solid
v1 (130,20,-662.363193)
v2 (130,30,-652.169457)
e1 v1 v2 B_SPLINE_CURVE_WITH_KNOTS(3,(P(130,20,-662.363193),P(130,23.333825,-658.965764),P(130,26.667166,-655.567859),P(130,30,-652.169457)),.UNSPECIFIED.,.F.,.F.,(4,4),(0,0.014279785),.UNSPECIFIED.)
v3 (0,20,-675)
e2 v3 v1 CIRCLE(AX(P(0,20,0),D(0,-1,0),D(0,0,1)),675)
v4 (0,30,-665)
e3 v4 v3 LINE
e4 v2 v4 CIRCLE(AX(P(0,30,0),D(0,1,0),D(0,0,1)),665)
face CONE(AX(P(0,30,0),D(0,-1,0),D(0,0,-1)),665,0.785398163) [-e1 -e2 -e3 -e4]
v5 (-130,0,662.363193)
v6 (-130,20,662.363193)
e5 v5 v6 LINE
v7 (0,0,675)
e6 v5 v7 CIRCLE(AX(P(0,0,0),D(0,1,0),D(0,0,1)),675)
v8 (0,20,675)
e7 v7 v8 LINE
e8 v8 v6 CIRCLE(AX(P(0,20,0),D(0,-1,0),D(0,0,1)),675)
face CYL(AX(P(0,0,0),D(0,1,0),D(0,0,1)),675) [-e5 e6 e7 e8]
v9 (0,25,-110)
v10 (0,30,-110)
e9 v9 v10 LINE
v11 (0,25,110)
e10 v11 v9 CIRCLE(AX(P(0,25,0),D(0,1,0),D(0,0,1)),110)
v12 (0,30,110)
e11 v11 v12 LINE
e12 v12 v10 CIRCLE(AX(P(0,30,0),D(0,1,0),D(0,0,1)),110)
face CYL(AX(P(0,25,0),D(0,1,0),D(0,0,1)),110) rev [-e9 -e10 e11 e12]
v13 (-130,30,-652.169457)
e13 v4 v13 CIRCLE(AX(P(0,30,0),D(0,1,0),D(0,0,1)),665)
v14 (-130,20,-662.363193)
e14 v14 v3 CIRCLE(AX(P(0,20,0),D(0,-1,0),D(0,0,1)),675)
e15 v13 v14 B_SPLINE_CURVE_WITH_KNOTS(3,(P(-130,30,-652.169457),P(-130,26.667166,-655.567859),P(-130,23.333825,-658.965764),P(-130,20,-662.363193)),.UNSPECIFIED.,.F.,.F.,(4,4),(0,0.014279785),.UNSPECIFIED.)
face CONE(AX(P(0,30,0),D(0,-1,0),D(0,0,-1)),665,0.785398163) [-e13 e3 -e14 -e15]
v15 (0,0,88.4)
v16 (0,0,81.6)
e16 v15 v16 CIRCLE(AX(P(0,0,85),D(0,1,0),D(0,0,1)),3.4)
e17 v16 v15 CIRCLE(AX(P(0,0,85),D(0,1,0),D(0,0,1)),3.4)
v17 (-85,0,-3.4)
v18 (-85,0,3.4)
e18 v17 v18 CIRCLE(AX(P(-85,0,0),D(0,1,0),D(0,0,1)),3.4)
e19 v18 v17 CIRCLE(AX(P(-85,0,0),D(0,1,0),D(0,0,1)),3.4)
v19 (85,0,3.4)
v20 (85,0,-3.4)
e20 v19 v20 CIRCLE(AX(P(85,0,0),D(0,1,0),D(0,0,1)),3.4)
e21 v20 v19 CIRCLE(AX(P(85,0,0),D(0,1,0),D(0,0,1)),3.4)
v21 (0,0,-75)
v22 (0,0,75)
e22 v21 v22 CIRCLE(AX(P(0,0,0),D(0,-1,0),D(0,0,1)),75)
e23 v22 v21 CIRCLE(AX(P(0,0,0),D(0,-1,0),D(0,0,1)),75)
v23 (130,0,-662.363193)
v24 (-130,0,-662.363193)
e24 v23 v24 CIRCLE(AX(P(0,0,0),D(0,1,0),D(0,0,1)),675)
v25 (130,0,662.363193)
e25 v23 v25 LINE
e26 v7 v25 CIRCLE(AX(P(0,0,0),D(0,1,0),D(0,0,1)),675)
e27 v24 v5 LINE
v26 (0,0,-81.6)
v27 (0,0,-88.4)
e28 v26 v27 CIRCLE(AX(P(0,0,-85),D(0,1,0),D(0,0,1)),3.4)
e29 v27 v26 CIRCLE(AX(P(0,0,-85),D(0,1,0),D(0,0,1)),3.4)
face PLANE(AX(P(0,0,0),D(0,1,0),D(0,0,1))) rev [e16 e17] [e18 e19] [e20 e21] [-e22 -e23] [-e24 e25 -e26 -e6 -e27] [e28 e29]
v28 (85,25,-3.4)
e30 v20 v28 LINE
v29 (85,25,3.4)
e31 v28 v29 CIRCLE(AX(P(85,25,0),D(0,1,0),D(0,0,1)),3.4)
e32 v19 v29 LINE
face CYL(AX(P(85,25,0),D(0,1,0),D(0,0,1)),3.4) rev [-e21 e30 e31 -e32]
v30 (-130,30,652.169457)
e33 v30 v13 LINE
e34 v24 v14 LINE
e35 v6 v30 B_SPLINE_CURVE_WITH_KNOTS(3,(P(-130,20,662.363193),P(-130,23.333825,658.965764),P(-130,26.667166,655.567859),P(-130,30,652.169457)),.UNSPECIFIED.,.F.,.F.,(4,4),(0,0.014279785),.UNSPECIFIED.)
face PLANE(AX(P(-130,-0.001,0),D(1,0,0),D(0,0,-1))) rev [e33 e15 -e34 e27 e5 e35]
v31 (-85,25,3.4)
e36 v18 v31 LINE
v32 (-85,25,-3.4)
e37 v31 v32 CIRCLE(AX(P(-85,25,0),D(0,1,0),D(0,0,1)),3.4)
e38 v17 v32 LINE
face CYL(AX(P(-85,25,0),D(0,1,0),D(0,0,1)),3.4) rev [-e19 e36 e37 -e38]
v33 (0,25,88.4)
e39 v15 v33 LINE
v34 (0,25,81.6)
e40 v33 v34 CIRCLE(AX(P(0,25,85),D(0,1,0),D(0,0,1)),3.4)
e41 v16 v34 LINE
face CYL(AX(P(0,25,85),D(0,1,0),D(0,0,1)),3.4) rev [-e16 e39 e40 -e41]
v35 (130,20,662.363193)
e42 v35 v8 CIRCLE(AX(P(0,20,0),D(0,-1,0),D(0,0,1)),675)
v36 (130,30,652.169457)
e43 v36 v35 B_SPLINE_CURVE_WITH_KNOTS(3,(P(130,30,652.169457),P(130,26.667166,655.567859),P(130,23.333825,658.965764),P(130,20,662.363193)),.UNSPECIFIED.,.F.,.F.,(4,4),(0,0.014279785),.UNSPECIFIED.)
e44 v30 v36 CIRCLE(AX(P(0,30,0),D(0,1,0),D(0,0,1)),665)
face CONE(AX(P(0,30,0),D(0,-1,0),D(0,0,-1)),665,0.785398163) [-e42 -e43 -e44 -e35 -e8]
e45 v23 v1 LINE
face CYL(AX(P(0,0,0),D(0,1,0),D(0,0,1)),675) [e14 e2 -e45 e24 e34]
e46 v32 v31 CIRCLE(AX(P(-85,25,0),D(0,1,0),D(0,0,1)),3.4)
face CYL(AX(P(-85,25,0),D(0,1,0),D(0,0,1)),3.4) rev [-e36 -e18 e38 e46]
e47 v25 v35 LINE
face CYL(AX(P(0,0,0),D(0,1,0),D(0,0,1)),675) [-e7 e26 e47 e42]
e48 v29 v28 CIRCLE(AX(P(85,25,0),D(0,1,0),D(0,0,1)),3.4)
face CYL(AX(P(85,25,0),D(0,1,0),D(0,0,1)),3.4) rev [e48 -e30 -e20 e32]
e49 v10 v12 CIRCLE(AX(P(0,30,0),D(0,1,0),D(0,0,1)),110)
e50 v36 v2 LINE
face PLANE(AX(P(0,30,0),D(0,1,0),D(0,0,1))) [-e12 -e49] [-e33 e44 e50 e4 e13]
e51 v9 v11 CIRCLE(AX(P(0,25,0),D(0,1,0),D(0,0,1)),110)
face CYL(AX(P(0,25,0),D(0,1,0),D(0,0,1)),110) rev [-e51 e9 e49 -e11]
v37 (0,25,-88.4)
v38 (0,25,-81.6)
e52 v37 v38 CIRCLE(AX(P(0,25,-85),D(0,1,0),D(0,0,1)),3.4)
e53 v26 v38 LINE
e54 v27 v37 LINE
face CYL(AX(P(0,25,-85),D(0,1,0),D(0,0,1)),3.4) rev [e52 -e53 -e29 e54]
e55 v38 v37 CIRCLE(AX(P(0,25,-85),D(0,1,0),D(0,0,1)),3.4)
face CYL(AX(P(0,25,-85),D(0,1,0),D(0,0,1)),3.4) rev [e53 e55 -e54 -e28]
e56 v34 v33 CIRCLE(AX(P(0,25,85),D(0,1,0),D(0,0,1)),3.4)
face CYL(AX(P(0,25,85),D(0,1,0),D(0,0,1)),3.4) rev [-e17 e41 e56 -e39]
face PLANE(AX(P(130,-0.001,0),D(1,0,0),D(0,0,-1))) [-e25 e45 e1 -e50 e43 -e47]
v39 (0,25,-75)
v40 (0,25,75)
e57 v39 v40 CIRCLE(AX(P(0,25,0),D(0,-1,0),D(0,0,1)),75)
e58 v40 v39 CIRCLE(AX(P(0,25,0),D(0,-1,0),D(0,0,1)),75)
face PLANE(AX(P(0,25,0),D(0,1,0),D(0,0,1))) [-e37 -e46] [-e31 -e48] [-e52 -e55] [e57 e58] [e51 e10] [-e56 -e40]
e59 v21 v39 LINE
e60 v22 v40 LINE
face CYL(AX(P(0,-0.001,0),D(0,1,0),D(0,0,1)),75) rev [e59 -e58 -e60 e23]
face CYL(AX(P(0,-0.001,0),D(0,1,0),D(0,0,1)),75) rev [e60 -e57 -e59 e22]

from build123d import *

# Parameters (mm, degrees)
SKETCH_1_R                = 810
EXTRUDE_1_DEPTH           = 25
SKETCH_2_R                = 730
EXTRUDE_2_DEPTH           = 5
CUT_EXTRUDE_1_REACH       = 1147.906
SKETCH_3_R                = 75
SKETCH_4_R                = 110
CUT_EXTRUDE_2_DEPTH       = 5
HOLE_WIZARD_M8_1_D        = 6.8
HOLE_WIZARD_25_5_25_5_1_D = 26
CUT_EXTRUDE_3_DEPTH       = 1146.905755287
CUT_EXTRUDE_3_DEPTH_BACK  = 1146.905755287
SKETCH_10_OUTSIDE_W       = 2080.244
SKETCH_10_OUTSIDE_H       = 2080.244
SKETCH_10_OUTSIDE_R       = 675
CHAMFER_1_SIZE            = 10


with BuildPart() as part:
    # 草图1 → 凸台-拉伸1 (new body)
    with BuildSketch(Plane(origin=(0, 0, 0), x_dir=(1, 0, 0), z_dir=(0, 1, 0))):
        with Locations(Location((0, 0, 0), (0, 0, 270))):
            Circle(SKETCH_1_R)
    extrude(amount=EXTRUDE_1_DEPTH)

    # 草图2 → 凸台-拉伸2 (add)
    with BuildSketch(Plane(origin=(0, 25, 0), x_dir=(1, 0, 0), z_dir=(0, 1, 0))):
        with Locations(Location((0, 0, 0), (0, 0, 270))):
            Circle(SKETCH_2_R)
    extrude(amount=EXTRUDE_2_DEPTH)

    # 草图3 → 切除-拉伸1 (cut, up to next)
    with BuildSketch(Plane(origin=(0, 30, 0), x_dir=(1, 0, 0), z_dir=(0, 1, 0)), mode=Mode.PRIVATE) as cut_extrude_1_sk1:
        with BuildLine():
            Line((130, 662.363193422), (130, -662.363193422))
            ThreePointArc((130, -662.363193422), (521.236510617, -428.879353665), (675, 0))
            ThreePointArc((675, 0), (521.236510617, 428.879353665), (130, 662.363193422))
        make_face()
    cut_extrude_1_tool1 = extrude(cut_extrude_1_sk1.sketch, amount=-CUT_EXTRUDE_1_REACH, mode=Mode.PRIVATE) & part.part
    # 草图3 → 切除-拉伸1 (cut, up to next)
    with BuildSketch(Plane(origin=(0, 30, 0), x_dir=(1, 0, 0), z_dir=(0, 1, 0)), mode=Mode.PRIVATE) as cut_extrude_1_sk2:
        with BuildLine():
            ThreePointArc((-130, 662.363193422), (-675, 0), (-130, -662.363193422))
            Line((-130, -662.363193422), (-130, 662.363193422))
        make_face()
    cut_extrude_1_tool2 = extrude(cut_extrude_1_sk2.sketch, amount=-CUT_EXTRUDE_1_REACH, mode=Mode.PRIVATE) & part.part
    # 草图3 → 切除-拉伸1 (cut, up to next)
    with BuildSketch(Plane(origin=(0, 30, 0), x_dir=(1, 0, 0), z_dir=(0, 1, 0)), mode=Mode.PRIVATE) as cut_extrude_1_sk3:
        with Locations(Location((0, 0, 0), (0, 0, 270))):
            Circle(SKETCH_3_R)
    cut_extrude_1_tool3 = extrude(cut_extrude_1_sk3.sketch, amount=-CUT_EXTRUDE_1_REACH, mode=Mode.PRIVATE) & part.part
    add(cut_extrude_1_tool1.solids().sort_by_distance((357.907844, 30, 0))[0], mode=Mode.SUBTRACT)
    add(cut_extrude_1_tool2.solids().sort_by_distance((-357.907844, 30, 0))[0], mode=Mode.SUBTRACT)
    add(cut_extrude_1_tool3.solids().sort_by_distance((0, 30, 0))[0], mode=Mode.SUBTRACT)

    # 草图4 → 切除-拉伸2 (cut)
    with BuildSketch(Plane(origin=(0, 30, 0), x_dir=(1, 0, 0), z_dir=(0, 1, 0))):
        with Locations(Location((0, 0, 0), (0, 0, 270))):
            Circle(SKETCH_4_R)
    extrude(amount=-CUT_EXTRUDE_2_DEPTH, mode=Mode.SUBTRACT)

    # M8 螺纹孔1 (through all)
    with Locations(Plane(origin=(0, 25, 0), x_dir=(1, 0, 0), z_dir=(0, 1, 0))):
        with Locations((0, 85), (85, 0), (0, -85), (-85, 0)):
            Hole(HOLE_WIZARD_M8_1_D / 2)

    # Ø25.5 (25.5) 直径孔1 (through all)
    with Locations(Plane(origin=(0, 25, 0), x_dir=(1, 0, 0), z_dir=(0, 1, 0))):
        with Locations((-59.354305918, 754.167962969), (59.354305918, 754.167962969), (176.601417757, 735.597844781), (289.500016584, 698.914866345), (395.270164208, 645.022284334), (491.307448562, 575.247112976), (575.247112976, 491.307448562), (645.022284334, 395.270164208), (698.914866345, 289.500016584), (735.597844781, 176.601417757), (754.167962969, 59.354305918), (754.167962969, -59.354305918), (735.597844781, -176.601417757), (698.914866345, -289.500016584), (645.022284334, -395.270164208), (575.247112976, -491.307448562), (491.307448562, -575.247112976), (395.270164208, -645.022284334), (289.500016584, -698.914866345), (176.601417757, -735.597844781), (59.354305918, -754.167962969), (-59.354305918, -754.167962969), (-176.601417757, -735.597844781), (-289.500016584, -698.914866345), (-395.270164208, -645.022284334), (-491.307448562, -575.247112976), (-575.247112976, -491.307448562), (-645.022284334, -395.270164208), (-698.914866345, -289.500016584), (-735.597844781, -176.601417757), (-754.167962969, -59.354305918), (-754.167962969, 59.354305918), (-735.597844781, 176.601417757), (-698.914866345, 289.500016584), (-645.022284334, 395.270164208), (-575.247112976, 491.307448562), (-491.307448562, 575.247112976), (-395.270164208, 645.022284334), (-289.500016584, 698.914866345), (-176.601417757, 735.597844781)):
            Hole(HOLE_WIZARD_25_5_25_5_1_D / 2)

    # 草图10 outside → 切除-拉伸3 (cut, two sides: drawn at the far end of the back side and taken through both)
    with BuildSketch(Plane(origin=(0, 30, 0), x_dir=(1, 0, 0), z_dir=(0, 1, 0)).offset(-CUT_EXTRUDE_3_DEPTH_BACK)):
        Rectangle(SKETCH_10_OUTSIDE_W, SKETCH_10_OUTSIDE_H)
        Circle(SKETCH_10_OUTSIDE_R, mode=Mode.SUBTRACT)
    extrude(amount=CUT_EXTRUDE_3_DEPTH + CUT_EXTRUDE_3_DEPTH_BACK, mode=Mode.SUBTRACT)

    # 倒角1
    chamfer_1_edges = [part.edges().sort_by_distance(p)[0] for p in [
        (0, 30, -675),
        (0, 30, 675),
    ]]
    chamfer(chamfer_1_edges, length=CHAMFER_1_SIZE)


solid = part.part
